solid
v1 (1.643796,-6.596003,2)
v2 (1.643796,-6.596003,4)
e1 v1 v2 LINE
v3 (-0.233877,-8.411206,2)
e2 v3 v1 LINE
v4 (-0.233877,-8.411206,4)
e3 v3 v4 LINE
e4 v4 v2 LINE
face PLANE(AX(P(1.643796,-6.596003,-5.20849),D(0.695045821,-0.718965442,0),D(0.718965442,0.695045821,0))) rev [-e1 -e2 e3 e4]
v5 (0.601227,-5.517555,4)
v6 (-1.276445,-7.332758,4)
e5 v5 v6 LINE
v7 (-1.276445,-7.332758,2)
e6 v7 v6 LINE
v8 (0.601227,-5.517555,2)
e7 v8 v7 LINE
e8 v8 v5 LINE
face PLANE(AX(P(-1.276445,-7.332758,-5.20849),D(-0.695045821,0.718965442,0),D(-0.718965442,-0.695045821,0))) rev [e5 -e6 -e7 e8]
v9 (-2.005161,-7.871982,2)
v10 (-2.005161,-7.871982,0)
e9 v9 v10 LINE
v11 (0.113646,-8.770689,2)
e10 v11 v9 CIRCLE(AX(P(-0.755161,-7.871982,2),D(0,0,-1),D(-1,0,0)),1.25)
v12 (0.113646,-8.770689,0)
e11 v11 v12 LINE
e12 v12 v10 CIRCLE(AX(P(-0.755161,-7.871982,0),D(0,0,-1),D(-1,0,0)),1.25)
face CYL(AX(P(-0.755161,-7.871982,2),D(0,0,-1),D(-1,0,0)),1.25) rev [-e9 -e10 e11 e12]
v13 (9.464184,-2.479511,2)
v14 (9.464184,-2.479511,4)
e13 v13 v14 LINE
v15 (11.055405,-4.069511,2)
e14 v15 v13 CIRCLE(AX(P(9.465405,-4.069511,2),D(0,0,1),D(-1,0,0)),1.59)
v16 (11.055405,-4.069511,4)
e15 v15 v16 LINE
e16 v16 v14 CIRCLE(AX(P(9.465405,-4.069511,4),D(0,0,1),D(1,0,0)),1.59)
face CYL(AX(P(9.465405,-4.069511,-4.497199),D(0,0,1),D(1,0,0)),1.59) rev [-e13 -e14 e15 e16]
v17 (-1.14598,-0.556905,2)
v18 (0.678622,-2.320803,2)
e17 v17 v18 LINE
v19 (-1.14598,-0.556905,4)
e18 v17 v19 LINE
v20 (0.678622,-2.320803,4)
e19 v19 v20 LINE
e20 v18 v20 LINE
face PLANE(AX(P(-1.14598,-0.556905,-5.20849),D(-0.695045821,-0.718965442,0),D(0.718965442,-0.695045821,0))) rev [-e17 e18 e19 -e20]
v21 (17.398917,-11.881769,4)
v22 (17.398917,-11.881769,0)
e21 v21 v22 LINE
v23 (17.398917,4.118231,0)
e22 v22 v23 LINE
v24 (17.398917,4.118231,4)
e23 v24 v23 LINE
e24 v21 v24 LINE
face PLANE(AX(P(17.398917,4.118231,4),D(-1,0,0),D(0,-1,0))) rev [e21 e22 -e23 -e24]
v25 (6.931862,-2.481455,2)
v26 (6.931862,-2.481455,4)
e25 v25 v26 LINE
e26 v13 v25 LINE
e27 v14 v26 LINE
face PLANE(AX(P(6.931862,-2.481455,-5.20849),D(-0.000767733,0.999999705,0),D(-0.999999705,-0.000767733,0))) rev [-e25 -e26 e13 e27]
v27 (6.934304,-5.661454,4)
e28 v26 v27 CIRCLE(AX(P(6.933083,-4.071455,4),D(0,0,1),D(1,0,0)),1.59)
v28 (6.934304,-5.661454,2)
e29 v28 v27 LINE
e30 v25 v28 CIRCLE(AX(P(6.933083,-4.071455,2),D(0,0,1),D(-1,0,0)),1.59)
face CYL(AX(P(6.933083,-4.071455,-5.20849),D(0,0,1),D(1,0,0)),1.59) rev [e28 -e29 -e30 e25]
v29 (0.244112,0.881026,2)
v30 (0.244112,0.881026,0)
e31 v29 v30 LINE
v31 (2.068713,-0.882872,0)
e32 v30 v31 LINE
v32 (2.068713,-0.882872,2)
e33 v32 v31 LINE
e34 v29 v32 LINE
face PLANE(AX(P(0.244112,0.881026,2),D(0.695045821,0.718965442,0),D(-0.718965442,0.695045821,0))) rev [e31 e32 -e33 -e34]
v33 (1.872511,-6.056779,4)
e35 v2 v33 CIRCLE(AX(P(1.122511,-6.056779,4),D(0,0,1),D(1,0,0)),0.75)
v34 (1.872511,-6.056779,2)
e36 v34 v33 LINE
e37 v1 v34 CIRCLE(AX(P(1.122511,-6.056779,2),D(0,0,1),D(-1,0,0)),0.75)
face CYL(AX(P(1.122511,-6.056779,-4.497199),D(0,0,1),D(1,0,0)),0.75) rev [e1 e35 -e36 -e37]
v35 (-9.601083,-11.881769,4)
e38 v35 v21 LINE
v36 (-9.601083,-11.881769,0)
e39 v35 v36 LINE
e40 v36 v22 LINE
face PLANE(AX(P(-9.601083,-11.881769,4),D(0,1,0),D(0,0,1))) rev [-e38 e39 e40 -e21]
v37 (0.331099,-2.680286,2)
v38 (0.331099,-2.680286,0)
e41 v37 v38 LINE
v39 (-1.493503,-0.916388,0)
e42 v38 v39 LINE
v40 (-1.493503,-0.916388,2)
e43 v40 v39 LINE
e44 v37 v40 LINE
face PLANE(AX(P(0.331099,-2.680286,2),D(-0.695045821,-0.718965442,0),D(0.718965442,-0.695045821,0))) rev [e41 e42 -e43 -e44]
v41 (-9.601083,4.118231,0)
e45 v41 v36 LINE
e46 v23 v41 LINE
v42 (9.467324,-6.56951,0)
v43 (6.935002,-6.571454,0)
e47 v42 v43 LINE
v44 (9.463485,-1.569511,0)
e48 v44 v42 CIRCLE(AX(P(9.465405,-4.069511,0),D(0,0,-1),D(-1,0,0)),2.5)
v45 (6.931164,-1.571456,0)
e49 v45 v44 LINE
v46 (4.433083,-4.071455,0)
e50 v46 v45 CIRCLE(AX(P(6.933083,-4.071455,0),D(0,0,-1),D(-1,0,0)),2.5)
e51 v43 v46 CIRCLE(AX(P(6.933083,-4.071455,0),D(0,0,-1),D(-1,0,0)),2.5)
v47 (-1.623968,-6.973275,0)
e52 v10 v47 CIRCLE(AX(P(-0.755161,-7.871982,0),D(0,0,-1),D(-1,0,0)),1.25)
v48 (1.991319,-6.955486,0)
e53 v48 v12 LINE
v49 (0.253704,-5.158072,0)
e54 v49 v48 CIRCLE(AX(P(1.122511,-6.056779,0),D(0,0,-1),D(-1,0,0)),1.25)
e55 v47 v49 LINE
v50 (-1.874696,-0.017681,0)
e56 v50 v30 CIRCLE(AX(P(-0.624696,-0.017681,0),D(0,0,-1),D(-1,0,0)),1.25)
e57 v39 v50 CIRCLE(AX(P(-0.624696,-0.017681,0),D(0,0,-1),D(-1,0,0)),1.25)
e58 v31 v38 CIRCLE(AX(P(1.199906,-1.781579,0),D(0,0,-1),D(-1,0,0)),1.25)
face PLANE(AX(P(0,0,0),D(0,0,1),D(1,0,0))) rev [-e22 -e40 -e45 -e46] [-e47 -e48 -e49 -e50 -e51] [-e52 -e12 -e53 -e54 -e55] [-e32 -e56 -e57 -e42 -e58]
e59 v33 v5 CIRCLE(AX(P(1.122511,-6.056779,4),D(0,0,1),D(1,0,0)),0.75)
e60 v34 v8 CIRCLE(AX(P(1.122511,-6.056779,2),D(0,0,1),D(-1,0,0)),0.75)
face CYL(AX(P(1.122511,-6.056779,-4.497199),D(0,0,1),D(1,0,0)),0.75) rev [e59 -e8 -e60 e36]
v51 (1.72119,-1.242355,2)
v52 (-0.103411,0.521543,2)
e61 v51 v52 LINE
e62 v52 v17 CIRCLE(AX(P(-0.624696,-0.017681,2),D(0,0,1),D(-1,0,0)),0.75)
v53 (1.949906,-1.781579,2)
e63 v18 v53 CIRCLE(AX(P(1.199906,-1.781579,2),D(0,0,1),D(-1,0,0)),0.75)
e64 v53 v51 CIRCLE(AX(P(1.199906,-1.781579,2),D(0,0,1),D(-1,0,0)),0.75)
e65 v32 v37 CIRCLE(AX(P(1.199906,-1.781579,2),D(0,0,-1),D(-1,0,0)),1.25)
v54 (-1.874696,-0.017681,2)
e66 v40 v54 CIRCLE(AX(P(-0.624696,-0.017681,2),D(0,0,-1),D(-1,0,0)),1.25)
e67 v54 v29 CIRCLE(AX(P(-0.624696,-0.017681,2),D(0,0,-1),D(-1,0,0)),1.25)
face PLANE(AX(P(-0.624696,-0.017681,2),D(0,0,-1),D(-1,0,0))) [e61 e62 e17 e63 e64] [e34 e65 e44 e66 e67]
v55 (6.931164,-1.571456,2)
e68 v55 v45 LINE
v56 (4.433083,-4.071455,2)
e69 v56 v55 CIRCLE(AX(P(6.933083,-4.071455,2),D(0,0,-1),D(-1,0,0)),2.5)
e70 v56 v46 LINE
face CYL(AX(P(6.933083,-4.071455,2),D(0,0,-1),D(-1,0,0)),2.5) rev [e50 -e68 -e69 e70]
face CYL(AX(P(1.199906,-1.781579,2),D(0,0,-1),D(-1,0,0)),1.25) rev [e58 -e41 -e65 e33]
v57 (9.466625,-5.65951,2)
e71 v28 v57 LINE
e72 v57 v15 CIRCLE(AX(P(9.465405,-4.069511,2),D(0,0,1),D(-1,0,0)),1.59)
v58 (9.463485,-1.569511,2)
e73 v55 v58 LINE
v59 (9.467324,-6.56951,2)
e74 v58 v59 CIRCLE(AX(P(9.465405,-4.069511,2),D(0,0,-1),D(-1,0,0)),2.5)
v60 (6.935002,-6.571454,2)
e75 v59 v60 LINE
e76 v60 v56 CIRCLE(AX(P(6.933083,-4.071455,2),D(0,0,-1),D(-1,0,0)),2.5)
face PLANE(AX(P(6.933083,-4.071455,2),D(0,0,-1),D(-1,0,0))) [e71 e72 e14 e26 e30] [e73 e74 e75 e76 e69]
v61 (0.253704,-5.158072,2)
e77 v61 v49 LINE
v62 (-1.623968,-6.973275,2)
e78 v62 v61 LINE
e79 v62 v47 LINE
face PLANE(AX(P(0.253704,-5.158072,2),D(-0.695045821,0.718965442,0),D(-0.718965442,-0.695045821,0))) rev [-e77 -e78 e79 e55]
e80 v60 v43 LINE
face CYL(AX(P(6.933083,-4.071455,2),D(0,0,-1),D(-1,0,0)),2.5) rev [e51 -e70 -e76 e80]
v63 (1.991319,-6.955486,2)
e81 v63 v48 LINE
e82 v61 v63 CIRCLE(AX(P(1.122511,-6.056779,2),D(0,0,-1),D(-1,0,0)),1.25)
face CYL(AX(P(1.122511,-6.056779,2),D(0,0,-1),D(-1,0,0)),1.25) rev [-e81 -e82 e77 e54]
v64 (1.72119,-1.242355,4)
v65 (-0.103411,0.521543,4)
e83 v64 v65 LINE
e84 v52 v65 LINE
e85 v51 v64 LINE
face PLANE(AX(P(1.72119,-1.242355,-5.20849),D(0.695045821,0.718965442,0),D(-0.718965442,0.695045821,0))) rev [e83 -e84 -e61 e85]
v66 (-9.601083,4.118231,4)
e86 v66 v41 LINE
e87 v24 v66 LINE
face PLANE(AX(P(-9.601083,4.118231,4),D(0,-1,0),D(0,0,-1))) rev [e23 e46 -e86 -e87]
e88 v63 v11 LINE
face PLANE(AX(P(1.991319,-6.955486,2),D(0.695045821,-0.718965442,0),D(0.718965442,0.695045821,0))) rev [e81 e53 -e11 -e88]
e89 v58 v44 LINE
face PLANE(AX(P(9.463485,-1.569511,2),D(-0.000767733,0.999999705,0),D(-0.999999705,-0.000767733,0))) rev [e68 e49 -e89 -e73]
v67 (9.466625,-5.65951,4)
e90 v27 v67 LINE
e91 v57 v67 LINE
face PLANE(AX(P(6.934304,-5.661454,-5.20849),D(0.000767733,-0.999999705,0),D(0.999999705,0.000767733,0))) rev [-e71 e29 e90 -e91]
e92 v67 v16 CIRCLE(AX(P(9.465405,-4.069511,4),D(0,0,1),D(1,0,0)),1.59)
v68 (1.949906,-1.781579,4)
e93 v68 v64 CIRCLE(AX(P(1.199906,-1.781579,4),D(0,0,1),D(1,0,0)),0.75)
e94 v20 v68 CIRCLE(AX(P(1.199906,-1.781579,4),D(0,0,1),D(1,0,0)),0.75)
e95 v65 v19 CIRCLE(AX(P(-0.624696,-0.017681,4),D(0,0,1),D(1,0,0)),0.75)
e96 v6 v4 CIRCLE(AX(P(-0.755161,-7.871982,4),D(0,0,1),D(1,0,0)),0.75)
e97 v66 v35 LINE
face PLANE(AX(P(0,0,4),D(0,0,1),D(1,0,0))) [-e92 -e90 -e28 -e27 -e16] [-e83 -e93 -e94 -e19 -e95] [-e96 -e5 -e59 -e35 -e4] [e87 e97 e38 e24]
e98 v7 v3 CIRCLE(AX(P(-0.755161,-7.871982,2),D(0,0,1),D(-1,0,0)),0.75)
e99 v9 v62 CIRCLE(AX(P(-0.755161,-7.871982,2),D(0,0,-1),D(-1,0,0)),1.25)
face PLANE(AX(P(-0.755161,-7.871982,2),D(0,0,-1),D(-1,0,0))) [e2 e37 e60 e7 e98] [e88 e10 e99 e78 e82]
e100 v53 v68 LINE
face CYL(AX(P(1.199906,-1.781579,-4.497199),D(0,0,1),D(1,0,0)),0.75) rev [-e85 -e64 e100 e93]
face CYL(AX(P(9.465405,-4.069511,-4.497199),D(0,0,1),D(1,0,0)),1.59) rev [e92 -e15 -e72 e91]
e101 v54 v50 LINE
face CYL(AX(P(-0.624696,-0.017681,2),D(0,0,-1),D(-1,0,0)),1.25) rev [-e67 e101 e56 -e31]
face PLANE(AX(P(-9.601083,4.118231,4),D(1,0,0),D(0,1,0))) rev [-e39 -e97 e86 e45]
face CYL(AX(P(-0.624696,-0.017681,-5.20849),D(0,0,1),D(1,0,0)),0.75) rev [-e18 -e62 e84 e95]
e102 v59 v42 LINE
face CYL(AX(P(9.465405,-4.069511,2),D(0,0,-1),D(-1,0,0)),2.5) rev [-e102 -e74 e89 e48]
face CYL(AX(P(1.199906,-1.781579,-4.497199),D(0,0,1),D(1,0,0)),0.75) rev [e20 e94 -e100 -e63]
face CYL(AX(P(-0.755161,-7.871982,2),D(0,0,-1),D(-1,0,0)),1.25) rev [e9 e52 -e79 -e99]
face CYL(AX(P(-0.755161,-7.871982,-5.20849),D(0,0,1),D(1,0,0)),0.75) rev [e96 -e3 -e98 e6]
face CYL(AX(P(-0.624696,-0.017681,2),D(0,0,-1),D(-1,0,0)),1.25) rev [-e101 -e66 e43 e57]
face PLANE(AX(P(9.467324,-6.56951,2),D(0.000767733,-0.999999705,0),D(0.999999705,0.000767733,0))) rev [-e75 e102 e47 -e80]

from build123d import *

# Parameters (mm, degrees)
SKETCH_1_W          = 27
SKETCH_1_H          = 16
EXTRUDE_1_DEPTH     = 4
SKETCH_2_R          = 0.75
SKETCH_2_R_2        = 1.59
CUT_EXTRUDE_2_DEPTH = 4
CUT_EXTRUDE_3_DEPTH = 4
CUT_EXTRUDE_4_DEPTH = 2


with BuildPart() as part:
    # 草图1 → 凸台-拉伸1 (new body)
    with BuildSketch(Plane.XY):
        with Locations((3.898916968, -3.881768953)):
            Rectangle(SKETCH_1_W, SKETCH_1_H)
    extrude(amount=EXTRUDE_1_DEPTH)

    # 草图2 → 切除-拉伸2 (cut)
    with BuildSketch(Plane.XY.offset(4)):
        with Locations((1.199905932, -1.781578746)):
            Circle(SKETCH_2_R)
        with Locations((1.122511443, -6.056778774)):
            Circle(SKETCH_2_R)
        with Locations((9.465404763, -4.069510677)):
            Circle(SKETCH_2_R_2)
    extrude(amount=-CUT_EXTRUDE_2_DEPTH, mode=Mode.SUBTRACT)

    # 草图3 → 切除-拉伸3 (cut)
    with BuildSketch(Plane.XY.offset(4)):
        with BuildLine():
            Line((6.931862452, -2.481455291), (9.464184068, -2.479511145))
            ThreePointArc((9.464184068, -2.479511145), (7.875405231, -4.070731371), (9.466625457, -5.659510208))
            Line((9.466625457, -5.659510208), (6.934303841, -5.661454354))
            ThreePointArc((6.934303841, -5.661454354), (5.343083615, -4.072675517), (6.931862452, -2.481455291))
        make_face()
        with BuildLine():
            Line((-1.276445305, -7.332757851), (0.601227077, -5.517554692))
            ThreePointArc((0.601227077, -5.517554692), (0.583287361, -6.578063139), (1.643795809, -6.596002856))
            Line((1.643795809, -6.596002856), (-0.233876574, -8.411206015))
            ThreePointArc((-0.233876574, -8.411206015), (-1.294385021, -8.393266299), (-1.276445305, -7.332757851))
        make_face()
        with BuildLine():
            Line((-1.145979965, -0.556904877), (0.678621567, -2.320802827))
            ThreePointArc((0.678621567, -2.320802827), (0.660681851, -1.26029438), (1.721190298, -1.242354664))
            Line((1.721190298, -1.242354664), (-0.103411234, 0.521543286))
            ThreePointArc((-0.103411234, 0.521543286), (-1.163919681, 0.50360357), (-1.145979965, -0.556904877))
        make_face()
    extrude(amount=-CUT_EXTRUDE_3_DEPTH, mode=Mode.SUBTRACT)

    # 草图5 → 切除-拉伸4 (cut)
    with BuildSketch(Plane(origin=(0, 0, 0), x_dir=(-1, 0, 0), z_dir=(0, 0, -1))):
        with BuildLine():
            Line((-9.463485432, -1.569511413), (-6.931163815, -1.57145556))
            ThreePointArc((-6.931163815, -1.57145556), (-4.433083883, -4.073374154), (-6.935002478, -6.571454086))
            Line((-6.935002478, -6.571454086), (-9.467324094, -6.56950994))
            ThreePointArc((-9.467324094, -6.56950994), (-11.965404026, -4.067591345), (-9.463485432, -1.569511413))
        make_face()
        with BuildLine():
            Line((-0.244111676, 0.881026007), (-2.068713208, -0.882871943))
            ThreePointArc((-2.068713208, -0.882871943), (-2.098612735, -2.650386022), (-0.331098657, -2.680285548))
            Line((-0.331098657, -2.680285548), (1.493502876, -0.916387599))
            ThreePointArc((1.493502876, -0.916387599), (1.523402402, 0.85112648), (-0.244111676, 0.881026007))
        make_face()
        with BuildLine():
            Line((-0.253704167, -5.158071971), (1.623968215, -6.97327513))
            ThreePointArc((1.623968215, -6.97327513), (1.653867742, -8.740789209), (-0.113646337, -8.770688736))
            Line((-0.113646337, -8.770688736), (-1.991318719, -6.955485577))
            ThreePointArc((-1.991318719, -6.955485577), (-2.021218246, -5.187971498), (-0.253704167, -5.158071971))
        make_face()
    extrude(amount=-CUT_EXTRUDE_4_DEPTH, mode=Mode.SUBTRACT)


solid = part.part
